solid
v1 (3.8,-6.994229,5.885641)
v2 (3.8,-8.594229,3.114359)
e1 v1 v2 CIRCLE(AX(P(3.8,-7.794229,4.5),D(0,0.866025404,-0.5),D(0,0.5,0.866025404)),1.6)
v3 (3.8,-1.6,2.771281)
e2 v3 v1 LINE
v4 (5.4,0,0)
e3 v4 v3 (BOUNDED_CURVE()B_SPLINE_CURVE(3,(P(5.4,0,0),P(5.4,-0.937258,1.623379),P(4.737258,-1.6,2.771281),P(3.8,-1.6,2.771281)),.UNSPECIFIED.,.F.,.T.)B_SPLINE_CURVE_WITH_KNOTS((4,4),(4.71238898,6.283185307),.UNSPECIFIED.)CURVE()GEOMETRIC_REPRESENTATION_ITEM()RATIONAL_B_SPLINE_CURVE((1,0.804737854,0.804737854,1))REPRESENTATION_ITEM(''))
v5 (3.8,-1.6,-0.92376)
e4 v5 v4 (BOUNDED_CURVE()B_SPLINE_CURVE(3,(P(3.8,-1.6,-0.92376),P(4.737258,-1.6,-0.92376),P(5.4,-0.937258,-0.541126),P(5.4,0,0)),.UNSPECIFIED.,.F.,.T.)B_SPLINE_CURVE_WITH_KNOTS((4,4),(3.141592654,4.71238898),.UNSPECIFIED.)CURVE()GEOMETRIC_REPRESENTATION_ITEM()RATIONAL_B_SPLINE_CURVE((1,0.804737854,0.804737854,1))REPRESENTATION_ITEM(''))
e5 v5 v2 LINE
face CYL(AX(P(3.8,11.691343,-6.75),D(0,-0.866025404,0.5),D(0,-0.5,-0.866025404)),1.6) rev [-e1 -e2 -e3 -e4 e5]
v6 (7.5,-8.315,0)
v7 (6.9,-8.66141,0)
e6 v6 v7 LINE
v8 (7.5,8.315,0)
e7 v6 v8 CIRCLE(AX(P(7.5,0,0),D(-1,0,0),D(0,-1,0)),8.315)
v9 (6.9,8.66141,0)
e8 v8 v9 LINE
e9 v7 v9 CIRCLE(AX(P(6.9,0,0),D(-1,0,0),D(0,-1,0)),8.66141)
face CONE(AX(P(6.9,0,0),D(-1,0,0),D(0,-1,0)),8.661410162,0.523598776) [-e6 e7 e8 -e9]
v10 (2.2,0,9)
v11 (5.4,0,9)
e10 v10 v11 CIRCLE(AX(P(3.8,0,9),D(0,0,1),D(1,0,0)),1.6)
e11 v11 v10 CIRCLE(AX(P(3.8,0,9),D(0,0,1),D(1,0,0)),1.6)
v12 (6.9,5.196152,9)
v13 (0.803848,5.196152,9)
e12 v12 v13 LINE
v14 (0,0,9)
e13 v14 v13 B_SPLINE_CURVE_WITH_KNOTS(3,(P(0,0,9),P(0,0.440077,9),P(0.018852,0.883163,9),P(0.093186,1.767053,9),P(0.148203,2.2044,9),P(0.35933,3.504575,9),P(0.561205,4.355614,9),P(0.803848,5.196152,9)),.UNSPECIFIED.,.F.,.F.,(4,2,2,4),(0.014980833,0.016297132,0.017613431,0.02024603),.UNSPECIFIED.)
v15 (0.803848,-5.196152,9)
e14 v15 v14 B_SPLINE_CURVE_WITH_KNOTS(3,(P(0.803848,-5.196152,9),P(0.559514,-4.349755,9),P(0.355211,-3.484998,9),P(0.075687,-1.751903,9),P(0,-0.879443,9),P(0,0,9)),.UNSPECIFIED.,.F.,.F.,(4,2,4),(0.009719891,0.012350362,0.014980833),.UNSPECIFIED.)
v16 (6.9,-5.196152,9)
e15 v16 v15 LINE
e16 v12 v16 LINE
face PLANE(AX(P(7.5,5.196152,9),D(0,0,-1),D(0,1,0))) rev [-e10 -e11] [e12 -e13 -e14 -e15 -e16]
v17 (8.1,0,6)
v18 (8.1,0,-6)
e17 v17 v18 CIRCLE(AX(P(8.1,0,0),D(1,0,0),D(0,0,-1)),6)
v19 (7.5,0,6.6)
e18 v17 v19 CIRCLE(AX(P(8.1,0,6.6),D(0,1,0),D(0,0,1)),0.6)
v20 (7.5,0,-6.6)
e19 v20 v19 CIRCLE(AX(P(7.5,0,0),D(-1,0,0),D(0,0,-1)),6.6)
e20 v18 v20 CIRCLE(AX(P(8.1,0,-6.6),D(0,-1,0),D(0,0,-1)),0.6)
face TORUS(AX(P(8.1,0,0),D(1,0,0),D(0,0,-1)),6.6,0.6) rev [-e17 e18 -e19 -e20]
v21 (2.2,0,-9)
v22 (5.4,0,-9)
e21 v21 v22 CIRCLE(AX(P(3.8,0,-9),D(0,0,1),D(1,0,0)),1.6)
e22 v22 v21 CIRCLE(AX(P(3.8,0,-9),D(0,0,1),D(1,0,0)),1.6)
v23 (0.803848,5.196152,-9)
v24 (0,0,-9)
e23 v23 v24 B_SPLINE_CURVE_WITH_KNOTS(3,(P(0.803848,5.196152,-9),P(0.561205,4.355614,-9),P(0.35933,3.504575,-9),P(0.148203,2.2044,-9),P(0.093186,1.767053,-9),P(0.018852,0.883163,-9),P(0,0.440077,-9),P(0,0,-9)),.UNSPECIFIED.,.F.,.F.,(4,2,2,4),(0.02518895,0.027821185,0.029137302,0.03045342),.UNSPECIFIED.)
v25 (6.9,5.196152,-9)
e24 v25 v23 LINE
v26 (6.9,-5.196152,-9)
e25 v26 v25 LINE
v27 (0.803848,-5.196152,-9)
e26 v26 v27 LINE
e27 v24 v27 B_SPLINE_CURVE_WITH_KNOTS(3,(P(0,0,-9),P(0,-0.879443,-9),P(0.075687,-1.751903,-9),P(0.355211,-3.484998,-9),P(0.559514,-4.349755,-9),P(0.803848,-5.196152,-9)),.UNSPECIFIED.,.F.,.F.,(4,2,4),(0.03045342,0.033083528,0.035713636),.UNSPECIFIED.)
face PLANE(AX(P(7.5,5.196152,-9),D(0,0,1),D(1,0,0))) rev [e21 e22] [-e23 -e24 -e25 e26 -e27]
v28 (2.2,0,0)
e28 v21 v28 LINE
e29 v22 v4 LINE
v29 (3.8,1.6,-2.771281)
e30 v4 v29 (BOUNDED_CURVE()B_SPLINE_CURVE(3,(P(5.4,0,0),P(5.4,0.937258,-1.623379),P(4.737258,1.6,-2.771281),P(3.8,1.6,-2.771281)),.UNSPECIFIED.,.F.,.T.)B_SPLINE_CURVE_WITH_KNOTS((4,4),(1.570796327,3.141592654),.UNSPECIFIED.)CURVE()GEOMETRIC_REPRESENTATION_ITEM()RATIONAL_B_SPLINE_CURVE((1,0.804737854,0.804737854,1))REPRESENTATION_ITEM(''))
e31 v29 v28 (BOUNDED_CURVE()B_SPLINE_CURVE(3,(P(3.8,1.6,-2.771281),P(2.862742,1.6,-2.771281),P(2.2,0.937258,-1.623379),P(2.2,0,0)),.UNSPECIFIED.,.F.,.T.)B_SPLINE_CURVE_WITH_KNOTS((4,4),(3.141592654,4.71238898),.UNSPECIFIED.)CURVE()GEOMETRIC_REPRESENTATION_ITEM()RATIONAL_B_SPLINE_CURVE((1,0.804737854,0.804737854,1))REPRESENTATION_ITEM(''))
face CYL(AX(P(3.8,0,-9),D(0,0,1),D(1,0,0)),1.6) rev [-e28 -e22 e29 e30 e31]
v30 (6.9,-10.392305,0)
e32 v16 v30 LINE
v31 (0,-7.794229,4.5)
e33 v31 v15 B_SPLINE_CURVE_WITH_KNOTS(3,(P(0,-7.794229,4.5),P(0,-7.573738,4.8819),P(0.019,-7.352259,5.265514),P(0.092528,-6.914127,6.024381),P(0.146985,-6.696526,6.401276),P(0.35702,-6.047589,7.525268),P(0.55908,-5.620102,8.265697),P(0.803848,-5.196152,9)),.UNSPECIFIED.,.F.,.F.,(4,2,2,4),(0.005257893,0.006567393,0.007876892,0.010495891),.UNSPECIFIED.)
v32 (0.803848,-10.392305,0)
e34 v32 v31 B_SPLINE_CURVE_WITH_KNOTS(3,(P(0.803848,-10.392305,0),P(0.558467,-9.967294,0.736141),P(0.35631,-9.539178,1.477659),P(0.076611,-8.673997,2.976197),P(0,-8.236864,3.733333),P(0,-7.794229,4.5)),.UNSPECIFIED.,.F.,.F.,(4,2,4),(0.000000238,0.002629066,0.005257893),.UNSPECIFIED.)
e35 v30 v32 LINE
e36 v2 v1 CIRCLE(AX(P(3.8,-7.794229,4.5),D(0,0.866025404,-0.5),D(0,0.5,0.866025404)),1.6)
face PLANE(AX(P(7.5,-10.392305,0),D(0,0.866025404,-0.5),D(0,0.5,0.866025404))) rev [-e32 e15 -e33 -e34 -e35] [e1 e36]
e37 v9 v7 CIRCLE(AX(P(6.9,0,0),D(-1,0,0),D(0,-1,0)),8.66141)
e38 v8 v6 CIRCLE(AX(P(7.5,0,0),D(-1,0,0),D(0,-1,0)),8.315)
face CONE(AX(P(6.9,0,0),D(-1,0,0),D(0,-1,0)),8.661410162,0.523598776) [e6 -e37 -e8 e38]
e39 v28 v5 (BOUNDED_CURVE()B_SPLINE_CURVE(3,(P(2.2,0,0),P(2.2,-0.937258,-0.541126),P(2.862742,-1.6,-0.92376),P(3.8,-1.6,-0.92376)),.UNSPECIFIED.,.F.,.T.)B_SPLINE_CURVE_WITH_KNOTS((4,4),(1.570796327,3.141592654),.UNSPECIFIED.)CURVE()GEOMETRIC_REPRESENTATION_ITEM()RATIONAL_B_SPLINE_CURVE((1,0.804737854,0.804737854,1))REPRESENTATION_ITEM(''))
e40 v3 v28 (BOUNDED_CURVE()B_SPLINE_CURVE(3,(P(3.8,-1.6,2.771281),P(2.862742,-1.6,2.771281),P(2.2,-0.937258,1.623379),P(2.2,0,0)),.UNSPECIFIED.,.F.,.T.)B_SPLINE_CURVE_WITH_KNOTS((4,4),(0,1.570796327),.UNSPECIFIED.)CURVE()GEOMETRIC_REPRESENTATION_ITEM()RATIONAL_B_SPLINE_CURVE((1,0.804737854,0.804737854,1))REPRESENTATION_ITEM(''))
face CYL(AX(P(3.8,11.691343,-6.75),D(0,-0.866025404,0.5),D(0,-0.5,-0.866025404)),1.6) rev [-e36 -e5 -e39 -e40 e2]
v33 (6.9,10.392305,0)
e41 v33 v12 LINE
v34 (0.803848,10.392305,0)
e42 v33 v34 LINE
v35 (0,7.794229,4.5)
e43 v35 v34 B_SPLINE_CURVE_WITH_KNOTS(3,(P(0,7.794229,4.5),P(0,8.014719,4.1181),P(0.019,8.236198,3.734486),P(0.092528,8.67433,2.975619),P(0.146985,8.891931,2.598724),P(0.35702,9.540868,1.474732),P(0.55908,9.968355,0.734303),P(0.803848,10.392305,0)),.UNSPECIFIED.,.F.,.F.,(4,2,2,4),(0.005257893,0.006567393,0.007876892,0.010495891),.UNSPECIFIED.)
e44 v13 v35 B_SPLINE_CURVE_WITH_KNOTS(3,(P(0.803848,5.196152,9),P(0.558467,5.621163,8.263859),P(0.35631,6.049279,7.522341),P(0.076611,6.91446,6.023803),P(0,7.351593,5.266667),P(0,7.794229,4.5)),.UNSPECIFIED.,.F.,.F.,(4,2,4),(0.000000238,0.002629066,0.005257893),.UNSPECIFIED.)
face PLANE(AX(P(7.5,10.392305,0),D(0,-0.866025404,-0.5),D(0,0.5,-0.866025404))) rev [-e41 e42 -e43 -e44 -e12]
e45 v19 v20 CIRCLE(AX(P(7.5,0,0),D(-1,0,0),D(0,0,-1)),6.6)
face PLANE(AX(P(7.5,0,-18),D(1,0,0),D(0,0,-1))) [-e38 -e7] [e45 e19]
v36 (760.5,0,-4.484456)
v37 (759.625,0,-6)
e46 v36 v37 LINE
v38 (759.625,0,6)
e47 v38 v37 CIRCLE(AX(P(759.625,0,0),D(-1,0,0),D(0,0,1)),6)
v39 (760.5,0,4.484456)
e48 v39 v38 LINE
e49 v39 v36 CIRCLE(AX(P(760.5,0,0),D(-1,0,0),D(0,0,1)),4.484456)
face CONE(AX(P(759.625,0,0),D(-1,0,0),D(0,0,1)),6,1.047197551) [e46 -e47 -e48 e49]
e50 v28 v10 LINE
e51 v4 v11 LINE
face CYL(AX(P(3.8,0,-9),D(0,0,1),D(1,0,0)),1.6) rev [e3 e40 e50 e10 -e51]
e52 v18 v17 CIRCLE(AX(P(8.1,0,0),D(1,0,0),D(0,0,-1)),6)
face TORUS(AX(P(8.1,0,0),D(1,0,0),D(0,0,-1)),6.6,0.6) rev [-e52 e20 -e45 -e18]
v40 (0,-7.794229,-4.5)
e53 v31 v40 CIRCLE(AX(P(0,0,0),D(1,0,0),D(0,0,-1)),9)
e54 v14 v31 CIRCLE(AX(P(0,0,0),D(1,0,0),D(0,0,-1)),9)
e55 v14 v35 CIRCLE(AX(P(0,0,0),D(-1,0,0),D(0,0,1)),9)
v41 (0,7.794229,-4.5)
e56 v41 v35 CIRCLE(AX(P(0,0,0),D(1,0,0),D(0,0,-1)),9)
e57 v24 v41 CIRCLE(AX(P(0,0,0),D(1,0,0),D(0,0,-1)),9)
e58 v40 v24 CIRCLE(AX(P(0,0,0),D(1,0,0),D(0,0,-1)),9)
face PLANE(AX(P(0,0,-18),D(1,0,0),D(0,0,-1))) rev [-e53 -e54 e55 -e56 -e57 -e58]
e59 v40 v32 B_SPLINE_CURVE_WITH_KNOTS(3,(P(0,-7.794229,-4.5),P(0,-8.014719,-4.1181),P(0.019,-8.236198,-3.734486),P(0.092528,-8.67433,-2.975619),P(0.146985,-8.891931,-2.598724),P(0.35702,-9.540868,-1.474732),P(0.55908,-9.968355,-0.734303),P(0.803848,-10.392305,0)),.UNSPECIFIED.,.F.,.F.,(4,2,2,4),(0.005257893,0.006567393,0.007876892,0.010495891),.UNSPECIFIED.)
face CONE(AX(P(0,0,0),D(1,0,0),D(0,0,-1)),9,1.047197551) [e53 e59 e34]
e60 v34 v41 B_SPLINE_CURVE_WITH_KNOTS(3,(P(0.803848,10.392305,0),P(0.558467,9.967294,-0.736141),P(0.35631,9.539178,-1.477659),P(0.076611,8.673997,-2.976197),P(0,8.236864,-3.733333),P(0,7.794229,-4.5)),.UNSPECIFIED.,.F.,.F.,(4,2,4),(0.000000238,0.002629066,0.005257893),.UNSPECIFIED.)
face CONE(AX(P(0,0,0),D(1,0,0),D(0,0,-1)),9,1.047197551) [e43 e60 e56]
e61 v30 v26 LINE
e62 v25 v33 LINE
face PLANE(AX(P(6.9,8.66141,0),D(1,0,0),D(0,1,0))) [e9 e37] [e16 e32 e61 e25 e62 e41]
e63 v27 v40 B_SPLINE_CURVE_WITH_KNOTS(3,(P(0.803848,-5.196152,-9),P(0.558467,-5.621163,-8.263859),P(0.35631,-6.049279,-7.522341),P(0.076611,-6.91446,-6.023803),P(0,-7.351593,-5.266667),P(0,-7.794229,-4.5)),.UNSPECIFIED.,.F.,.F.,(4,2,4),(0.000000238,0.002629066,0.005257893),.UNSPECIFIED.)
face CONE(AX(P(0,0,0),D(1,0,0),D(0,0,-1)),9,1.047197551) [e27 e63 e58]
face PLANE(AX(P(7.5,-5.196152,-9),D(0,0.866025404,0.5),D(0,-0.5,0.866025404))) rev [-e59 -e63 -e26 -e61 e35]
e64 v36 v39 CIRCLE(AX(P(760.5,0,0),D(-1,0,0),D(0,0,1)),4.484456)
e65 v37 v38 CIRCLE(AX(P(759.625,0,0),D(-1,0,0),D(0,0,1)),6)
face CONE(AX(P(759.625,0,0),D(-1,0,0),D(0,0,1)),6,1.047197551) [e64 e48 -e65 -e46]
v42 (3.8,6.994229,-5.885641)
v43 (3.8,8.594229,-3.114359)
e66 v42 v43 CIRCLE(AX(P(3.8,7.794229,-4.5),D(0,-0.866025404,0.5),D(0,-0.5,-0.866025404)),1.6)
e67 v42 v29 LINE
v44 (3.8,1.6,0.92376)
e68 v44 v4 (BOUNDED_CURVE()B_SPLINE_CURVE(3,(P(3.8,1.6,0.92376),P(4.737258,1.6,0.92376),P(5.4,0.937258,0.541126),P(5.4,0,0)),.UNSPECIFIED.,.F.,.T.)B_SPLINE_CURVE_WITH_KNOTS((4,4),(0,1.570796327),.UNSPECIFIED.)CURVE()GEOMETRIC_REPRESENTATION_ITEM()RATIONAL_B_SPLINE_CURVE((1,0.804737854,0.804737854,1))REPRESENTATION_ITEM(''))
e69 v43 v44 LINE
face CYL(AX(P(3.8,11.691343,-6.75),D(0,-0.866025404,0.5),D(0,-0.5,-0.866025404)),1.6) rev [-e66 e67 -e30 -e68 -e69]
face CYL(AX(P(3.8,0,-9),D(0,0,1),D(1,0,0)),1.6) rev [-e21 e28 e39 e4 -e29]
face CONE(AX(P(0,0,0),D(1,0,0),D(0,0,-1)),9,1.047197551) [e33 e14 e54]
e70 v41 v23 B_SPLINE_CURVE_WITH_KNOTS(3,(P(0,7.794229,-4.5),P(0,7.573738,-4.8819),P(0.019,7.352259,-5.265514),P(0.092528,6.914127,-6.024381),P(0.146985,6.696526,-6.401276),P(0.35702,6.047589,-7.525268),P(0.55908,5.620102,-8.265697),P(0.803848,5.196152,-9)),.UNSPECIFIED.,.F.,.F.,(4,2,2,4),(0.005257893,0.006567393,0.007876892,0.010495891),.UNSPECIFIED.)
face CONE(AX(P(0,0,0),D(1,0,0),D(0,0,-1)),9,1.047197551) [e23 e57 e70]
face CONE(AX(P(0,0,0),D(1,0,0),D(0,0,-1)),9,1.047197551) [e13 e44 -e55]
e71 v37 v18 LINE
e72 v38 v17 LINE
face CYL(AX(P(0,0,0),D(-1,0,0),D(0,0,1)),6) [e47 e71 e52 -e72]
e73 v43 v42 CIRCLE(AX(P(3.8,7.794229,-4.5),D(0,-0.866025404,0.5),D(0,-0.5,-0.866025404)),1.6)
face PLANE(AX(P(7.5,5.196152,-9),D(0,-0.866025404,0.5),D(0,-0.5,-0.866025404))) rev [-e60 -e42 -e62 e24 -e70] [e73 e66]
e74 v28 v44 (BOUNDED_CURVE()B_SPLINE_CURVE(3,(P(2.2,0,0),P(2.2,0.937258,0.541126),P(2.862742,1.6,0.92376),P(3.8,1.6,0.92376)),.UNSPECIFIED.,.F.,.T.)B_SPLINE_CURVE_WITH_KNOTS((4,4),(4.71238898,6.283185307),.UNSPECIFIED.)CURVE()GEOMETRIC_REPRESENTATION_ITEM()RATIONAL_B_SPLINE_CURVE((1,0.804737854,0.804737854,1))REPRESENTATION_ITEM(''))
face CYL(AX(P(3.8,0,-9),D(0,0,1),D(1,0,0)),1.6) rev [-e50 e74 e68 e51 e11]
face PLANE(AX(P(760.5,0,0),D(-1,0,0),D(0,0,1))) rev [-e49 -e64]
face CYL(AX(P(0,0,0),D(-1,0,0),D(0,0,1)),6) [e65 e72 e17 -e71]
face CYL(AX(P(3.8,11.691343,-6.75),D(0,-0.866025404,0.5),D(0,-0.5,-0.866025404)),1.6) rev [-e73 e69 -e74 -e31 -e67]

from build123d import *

# Parameters (mm, degrees)
EXTRUDE_405_DEPTH        = 7.5
FILLET_1252_R            = 0.6
SKETCH_7_R               = 1.6
CUT_EXTRUDE_1_DEPTH      = 761.624250205
PATTERN_CIRCULAR_1_COUNT = 2
PATTERN_CIRCULAR_1_ANGLE = 60


with BuildPart() as part:
    # 草图1 → Extrude 405 (new body)
    with BuildSketch(Plane(origin=(0, 0, 0), x_dir=(0, 0, -1), z_dir=(1, 0, 0))):
        Polygon((9, 5.196152423), (9, -5.196152423), (0, -10.392304845), (-9, -5.196152423), (-9, 5.196152423), (0, 10.392304845), align=None)
    extrude(amount=EXTRUDE_405_DEPTH)

    # 草图2 → 凸台-旋转1 (revolve)
    with BuildSketch(Plane.XY, mode=Mode.PRIVATE) as revolve_1_sk:
        Polygon((0, 0), (760.5, 0), (760.5, 4.4845), (760.5, 6), (730.5, 6), (0, 6), align=None)
    revolve(revolve_1_sk.sketch.rotate(Axis((0, 0, 0), (1, 0, 0)), 90), axis=Axis((0, 0, 0), (1, 0, 0)))

    # 草图3 → 切除-旋转1 (revolve, cut)
    with BuildSketch(Plane.XY):
        Polygon((0, 9), (3.690598923, 15.392304845), (3.690598923, 20.392304845), (-10, 20.392304845), (-10, 9), align=None)
    revolve(axis=Axis((0, 0, 0), (1, 0, 0)), mode=Mode.SUBTRACT)

    # 草图5 → 切除-旋转5 (revolve, cut)
    with BuildSketch(Plane.XY, mode=Mode.PRIVATE) as cut_revolve_5_sk:
        Polygon((7.5, 8.315), (6.9, 8.661410162), (6.9, 10.392304845), (7.5, 10.392304845), align=None)
    revolve(cut_revolve_5_sk.sketch.rotate(Axis((0, 0, 0), (1, 0, 0)), 180), axis=Axis((0, 0, 0), (1, 0, 0)), mode=Mode.SUBTRACT)

    # Fillet 1252
    fillet_1252_edges = [part.edges().sort_by_distance(p)[0] for p in [
        (7.5, 0, -6),
    ]]
    fillet(fillet_1252_edges, radius=FILLET_1252_R)

    # 草图6 → 切除-旋转4 (revolve, cut)
    with BuildSketch(Plane.XY, mode=Mode.PRIVATE) as cut_revolve_4_sk:
        Polygon((759.625, 6), (761.375, 6), (760.5, 4.484455543), align=None)
    revolve(cut_revolve_4_sk.sketch.rotate(Axis((0, 0, 0), (1, 0, 0)), 90), axis=Axis((0, 0, 0), (1, 0, 0)), mode=Mode.SUBTRACT)

    # 草图7 → 切除-拉伸1 (cut, symmetric)
    with BuildSketch(Plane.XY):
        with Locations((3.8, 0)):
            Circle(SKETCH_7_R)
    cut_extrude_1 = extrude(amount=CUT_EXTRUDE_1_DEPTH, both=True, mode=Mode.SUBTRACT)

    # 阵列(圆周)1: 切除-拉伸1 ×2 about axis
    pattern_circular_1_axis = Axis((0, 0, 0), (1, 0, 0))
    for i in range(1, PATTERN_CIRCULAR_1_COUNT):
        add(cut_extrude_1.rotate(pattern_circular_1_axis, i * PATTERN_CIRCULAR_1_ANGLE / (PATTERN_CIRCULAR_1_COUNT - 1)), mode=Mode.SUBTRACT)


solid = part.part
